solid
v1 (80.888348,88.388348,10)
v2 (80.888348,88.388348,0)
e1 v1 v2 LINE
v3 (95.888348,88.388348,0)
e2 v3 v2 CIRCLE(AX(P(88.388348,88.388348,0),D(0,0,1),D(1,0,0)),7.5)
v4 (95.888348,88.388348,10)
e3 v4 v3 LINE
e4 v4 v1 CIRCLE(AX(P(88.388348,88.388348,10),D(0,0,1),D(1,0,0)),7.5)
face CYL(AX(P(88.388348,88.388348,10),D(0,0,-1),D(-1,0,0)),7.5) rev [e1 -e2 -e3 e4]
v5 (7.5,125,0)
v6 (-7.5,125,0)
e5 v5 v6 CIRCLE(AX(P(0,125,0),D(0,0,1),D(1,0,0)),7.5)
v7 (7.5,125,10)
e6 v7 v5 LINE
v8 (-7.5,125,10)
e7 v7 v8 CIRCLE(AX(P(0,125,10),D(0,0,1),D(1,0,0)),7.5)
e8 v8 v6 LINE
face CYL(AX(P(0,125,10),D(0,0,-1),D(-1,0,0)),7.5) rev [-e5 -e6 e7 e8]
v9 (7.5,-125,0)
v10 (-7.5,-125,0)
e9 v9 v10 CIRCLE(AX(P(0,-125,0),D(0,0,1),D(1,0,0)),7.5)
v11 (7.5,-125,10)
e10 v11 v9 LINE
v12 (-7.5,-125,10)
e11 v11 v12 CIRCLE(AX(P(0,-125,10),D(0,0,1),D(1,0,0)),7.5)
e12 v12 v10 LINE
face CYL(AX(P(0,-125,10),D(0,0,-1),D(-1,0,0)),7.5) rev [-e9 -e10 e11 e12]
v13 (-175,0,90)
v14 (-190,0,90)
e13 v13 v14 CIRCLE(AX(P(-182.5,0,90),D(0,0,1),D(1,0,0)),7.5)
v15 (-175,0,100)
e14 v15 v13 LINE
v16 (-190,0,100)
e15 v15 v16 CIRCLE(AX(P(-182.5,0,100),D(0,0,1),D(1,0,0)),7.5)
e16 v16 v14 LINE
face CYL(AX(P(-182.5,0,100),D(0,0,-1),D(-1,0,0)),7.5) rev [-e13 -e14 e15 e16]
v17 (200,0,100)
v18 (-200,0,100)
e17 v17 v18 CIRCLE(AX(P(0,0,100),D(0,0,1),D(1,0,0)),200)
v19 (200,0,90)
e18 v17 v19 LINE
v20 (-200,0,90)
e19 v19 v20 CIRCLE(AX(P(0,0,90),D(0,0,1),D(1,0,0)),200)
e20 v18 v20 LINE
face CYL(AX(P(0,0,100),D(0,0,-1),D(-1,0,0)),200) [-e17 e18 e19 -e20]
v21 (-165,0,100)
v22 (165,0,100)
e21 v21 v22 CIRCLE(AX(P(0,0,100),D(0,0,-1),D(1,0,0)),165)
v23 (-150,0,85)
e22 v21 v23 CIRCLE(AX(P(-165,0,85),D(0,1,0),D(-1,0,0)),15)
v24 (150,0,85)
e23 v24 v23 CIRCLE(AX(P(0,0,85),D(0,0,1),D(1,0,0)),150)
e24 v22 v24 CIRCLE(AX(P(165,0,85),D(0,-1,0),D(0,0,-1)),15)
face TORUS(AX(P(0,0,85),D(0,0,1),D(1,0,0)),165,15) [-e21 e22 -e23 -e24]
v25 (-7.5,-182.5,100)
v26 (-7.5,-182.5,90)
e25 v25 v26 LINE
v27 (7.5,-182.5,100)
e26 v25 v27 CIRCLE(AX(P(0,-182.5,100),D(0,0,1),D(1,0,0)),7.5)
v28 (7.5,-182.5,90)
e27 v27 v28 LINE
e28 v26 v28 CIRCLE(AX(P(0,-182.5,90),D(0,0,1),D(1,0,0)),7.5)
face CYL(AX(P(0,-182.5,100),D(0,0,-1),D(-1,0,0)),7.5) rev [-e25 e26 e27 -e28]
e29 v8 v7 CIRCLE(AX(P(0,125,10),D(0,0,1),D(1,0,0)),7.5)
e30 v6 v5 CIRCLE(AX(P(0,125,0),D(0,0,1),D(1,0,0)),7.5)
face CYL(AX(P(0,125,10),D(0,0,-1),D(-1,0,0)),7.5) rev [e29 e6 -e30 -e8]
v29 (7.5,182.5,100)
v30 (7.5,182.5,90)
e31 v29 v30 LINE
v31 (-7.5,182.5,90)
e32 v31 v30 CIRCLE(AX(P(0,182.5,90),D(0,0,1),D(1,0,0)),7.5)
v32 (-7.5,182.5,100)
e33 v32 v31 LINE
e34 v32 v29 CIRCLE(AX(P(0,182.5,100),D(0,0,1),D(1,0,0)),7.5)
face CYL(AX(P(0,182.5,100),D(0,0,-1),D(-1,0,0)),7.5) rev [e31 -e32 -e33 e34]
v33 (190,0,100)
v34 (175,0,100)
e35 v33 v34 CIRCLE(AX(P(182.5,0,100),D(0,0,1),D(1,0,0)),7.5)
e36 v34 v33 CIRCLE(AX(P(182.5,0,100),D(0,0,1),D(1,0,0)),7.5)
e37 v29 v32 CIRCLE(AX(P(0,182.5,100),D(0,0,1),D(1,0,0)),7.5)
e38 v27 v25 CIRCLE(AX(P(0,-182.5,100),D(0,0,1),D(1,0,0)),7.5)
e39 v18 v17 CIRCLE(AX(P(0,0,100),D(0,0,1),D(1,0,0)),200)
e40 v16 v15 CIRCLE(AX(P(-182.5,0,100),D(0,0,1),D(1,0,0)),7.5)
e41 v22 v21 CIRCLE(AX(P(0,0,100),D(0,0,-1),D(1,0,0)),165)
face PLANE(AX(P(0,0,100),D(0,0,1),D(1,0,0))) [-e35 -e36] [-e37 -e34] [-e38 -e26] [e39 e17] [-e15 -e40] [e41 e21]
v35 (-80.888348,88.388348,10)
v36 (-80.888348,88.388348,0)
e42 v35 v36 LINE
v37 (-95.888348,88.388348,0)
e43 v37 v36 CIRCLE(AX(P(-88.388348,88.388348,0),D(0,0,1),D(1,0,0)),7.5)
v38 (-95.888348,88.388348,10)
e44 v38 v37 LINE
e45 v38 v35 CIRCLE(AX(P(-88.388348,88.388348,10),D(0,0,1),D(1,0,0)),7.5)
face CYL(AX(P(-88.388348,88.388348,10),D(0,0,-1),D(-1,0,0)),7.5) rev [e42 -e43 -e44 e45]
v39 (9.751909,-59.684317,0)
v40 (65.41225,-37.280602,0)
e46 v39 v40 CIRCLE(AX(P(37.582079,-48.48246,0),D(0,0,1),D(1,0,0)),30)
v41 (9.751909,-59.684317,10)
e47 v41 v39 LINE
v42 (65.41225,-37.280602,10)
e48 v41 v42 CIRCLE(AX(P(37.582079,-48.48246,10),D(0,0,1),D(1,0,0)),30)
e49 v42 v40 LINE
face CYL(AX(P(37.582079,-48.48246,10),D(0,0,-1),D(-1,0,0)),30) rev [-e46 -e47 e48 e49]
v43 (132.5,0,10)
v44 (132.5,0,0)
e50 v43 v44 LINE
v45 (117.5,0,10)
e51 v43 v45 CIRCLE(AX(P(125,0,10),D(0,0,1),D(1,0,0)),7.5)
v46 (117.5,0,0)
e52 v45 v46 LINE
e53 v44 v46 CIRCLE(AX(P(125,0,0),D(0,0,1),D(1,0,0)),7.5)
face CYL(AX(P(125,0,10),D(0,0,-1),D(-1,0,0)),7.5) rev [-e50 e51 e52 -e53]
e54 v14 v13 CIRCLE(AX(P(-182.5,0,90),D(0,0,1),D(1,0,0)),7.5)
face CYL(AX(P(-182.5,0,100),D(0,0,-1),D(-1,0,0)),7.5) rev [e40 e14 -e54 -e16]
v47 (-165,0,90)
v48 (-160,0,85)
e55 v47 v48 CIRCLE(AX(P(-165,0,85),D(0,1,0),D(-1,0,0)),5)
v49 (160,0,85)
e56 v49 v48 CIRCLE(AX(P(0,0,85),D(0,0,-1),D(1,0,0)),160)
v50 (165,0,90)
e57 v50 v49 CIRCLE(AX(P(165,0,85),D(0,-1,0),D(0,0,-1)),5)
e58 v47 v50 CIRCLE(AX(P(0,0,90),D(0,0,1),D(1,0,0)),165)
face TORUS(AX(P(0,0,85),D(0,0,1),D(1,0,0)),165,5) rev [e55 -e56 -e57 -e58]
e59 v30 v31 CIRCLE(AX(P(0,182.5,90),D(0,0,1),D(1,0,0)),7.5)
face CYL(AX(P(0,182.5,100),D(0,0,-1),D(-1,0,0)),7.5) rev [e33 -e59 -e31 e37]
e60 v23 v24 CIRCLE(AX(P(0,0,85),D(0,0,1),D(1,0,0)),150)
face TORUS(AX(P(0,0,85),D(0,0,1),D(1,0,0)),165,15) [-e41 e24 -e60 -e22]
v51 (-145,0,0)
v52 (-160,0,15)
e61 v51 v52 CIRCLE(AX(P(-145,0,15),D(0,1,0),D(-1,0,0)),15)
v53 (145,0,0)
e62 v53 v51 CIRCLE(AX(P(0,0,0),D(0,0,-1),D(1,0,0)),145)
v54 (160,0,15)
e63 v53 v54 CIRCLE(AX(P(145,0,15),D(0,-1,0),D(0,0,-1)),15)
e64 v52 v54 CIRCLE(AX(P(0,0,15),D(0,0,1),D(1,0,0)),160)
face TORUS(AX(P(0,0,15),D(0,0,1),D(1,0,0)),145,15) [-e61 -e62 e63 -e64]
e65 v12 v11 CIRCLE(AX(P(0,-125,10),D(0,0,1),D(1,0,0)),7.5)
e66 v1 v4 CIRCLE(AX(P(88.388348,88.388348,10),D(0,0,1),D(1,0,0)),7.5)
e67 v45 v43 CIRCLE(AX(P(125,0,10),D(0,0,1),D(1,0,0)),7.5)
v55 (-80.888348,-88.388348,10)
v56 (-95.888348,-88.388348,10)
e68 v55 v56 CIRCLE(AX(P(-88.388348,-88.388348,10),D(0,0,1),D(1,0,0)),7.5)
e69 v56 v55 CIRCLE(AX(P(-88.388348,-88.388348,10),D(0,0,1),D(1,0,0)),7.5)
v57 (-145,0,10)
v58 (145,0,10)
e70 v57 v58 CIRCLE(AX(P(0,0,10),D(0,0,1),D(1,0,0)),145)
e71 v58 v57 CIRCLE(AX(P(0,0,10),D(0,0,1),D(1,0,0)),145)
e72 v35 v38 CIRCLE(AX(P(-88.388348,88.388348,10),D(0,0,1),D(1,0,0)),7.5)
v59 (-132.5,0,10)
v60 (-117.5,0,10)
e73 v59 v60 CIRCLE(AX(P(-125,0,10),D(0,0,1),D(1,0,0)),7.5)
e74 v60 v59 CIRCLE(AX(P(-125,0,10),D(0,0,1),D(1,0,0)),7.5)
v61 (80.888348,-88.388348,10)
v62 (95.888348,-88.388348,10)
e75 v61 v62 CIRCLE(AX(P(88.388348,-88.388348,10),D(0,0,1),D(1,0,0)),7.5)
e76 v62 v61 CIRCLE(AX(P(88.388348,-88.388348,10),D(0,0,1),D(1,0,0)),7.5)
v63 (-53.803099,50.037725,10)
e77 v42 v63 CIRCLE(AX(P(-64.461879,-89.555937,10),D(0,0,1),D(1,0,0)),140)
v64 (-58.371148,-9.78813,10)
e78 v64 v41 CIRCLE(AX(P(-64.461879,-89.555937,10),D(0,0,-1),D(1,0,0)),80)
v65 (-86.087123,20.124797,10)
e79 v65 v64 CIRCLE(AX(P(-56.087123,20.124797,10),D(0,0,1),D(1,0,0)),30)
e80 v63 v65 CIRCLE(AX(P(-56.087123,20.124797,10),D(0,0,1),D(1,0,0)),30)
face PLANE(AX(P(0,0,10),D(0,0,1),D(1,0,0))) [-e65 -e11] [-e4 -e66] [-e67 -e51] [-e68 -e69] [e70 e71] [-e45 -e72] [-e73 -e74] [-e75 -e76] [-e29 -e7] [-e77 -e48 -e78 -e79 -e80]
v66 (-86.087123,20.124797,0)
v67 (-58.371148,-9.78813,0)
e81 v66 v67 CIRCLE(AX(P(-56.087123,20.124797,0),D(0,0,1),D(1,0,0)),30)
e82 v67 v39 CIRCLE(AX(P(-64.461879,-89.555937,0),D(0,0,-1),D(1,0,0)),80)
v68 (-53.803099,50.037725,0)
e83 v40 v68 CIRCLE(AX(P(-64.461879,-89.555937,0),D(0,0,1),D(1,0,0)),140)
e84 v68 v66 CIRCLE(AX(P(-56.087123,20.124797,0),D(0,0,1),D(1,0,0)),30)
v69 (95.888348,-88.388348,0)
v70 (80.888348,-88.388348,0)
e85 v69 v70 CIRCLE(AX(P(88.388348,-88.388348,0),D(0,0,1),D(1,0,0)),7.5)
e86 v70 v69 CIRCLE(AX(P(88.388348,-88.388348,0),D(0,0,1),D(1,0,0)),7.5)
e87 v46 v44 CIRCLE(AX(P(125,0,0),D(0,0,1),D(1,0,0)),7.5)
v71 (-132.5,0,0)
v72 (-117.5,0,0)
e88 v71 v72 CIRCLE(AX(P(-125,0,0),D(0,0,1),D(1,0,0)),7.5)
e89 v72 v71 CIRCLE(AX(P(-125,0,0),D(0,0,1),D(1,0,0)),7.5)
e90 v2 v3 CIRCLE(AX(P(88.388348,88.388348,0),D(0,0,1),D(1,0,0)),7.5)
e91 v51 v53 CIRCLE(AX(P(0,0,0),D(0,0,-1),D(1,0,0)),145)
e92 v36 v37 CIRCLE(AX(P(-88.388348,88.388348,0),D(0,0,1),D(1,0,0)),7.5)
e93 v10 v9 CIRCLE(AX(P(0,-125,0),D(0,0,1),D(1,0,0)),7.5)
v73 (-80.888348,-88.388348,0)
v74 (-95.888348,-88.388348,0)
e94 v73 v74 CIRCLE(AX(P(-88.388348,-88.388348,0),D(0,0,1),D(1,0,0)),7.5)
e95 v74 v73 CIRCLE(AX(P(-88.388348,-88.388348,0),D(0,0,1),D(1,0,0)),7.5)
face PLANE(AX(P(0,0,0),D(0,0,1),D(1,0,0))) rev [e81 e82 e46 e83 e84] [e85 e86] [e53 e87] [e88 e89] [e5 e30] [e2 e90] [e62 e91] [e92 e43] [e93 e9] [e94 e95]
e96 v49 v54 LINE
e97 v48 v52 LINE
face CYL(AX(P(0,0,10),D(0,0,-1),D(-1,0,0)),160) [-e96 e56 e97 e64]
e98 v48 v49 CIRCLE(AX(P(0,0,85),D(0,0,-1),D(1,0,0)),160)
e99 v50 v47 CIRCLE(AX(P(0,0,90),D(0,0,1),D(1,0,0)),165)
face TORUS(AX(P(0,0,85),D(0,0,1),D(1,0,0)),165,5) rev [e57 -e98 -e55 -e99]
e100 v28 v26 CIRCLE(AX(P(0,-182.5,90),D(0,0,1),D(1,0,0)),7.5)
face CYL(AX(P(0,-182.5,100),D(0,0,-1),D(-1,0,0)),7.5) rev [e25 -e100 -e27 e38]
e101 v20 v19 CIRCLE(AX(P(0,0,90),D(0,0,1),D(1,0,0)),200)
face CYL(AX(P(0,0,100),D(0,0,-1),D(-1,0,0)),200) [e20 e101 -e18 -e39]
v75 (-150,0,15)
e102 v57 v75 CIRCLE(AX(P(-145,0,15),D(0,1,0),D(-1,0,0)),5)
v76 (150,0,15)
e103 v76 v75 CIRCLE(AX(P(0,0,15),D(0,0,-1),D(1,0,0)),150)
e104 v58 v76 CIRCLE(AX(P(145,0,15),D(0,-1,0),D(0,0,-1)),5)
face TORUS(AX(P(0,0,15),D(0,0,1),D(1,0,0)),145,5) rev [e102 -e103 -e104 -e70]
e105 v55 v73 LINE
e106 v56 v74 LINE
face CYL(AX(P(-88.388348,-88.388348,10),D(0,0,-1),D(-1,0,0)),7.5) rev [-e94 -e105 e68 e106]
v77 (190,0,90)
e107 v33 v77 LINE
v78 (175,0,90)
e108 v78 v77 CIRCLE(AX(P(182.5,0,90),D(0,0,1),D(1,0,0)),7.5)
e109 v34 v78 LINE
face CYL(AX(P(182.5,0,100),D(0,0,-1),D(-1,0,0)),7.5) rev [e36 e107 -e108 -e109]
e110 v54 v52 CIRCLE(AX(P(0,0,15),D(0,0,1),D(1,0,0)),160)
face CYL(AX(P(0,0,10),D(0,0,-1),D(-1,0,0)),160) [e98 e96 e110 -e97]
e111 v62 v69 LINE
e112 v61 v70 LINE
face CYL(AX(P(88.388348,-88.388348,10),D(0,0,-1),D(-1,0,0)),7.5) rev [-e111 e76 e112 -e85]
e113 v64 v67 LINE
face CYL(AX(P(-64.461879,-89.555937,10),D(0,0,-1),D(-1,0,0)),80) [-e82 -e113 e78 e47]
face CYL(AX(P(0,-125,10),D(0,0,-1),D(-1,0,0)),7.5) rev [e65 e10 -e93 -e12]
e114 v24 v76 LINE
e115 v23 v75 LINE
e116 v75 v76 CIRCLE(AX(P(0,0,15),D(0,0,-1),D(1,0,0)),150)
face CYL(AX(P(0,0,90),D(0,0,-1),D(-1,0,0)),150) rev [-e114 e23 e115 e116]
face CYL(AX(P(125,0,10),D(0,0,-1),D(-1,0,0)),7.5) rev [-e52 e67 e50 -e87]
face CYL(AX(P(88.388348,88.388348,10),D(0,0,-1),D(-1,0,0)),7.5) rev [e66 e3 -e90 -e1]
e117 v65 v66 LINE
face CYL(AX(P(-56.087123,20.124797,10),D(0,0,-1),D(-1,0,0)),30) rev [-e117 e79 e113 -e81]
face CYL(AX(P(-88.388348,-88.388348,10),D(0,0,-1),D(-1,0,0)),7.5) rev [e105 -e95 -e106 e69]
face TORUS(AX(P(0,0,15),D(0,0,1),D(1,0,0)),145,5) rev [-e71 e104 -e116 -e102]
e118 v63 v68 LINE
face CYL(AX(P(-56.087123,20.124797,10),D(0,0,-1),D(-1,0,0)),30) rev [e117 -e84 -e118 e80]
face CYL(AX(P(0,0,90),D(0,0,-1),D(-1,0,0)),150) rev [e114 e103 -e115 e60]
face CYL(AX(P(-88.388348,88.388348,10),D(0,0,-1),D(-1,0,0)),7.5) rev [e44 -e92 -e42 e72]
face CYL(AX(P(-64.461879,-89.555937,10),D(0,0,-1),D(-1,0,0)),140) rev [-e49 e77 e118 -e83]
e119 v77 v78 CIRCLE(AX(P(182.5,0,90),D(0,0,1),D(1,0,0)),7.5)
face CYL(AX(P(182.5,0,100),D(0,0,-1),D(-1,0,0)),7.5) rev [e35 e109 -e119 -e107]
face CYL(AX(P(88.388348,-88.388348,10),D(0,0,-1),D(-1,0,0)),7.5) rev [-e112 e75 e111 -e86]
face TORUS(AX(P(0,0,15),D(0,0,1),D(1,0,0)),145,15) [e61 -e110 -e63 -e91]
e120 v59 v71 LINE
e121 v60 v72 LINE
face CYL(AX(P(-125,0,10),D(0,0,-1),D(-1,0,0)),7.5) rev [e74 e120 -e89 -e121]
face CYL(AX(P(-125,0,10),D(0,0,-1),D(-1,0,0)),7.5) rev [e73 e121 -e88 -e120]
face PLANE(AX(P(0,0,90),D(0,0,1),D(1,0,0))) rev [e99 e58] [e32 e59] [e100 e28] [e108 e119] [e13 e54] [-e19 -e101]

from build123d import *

# Parameters (mm, degrees)
SKETCH1_R           = 160
SKETCH1_R_2         = 7.5
BOSS_EXTRUDE1_DEPTH = 10
SKETCH2_R           = 160
SKETCH2_R_2         = 150
BOSS_EXTRUDE2_DEPTH = 80
SKETCH3_R           = 200
SKETCH3_R_2         = 150
SKETCH3_R_3         = 7.5
BOSS_EXTRUDE3_DEPTH = 10
FILLET1_R           = 5
FILLET2_R           = 15


with BuildPart() as part:
    # Sketch1 → Boss-Extrude1 (new body)
    with BuildSketch(Plane.XY):
        Circle(SKETCH1_R)
        with Locations((0, 125)):
            Circle(SKETCH1_R_2, mode=Mode.SUBTRACT)
        with Locations((88.388347648, 88.388347648)):
            Circle(SKETCH1_R_2, mode=Mode.SUBTRACT)
        with Locations((125, 0)):
            Circle(SKETCH1_R_2, mode=Mode.SUBTRACT)
        with Locations((88.388347648, -88.388347648)):
            Circle(SKETCH1_R_2, mode=Mode.SUBTRACT)
        with Locations((0, -125)):
            Circle(SKETCH1_R_2, mode=Mode.SUBTRACT)
        with Locations((-88.388347648, -88.388347648)):
            Circle(SKETCH1_R_2, mode=Mode.SUBTRACT)
        with Locations((-125, 0)):
            Circle(SKETCH1_R_2, mode=Mode.SUBTRACT)
        with Locations((-88.388347648, 88.388347648)):
            Circle(SKETCH1_R_2, mode=Mode.SUBTRACT)
        with BuildLine():
            ThreePointArc((-53.803098946, 50.037724546), (-86.000050805, 22.408821364), (-58.371147623, -9.788130495))
            ThreePointArc((-58.371147623, -9.788130495), (-17.190203431, -25.016114851), (9.751908775, -59.684317313))
            ThreePointArc((9.751908775, -59.684317313), (48.783936726, -76.312630338), (65.412249751, -37.280602387))
            ThreePointArc((65.412249751, -37.280602387), (18.26355339, 23.388751922), (-53.803098946, 50.037724546))
        make_face(mode=Mode.SUBTRACT)
    extrude(amount=BOSS_EXTRUDE1_DEPTH)

    # Sketch2 → Boss-Extrude2 (add)
    with BuildSketch(Plane.XY.offset(10)):
        Circle(SKETCH2_R)
        Circle(SKETCH2_R_2, mode=Mode.SUBTRACT)
    extrude(amount=BOSS_EXTRUDE2_DEPTH)

    # Sketch3 → Boss-Extrude3 (add)
    with BuildSketch(Plane.XY.offset(90)):
        Circle(SKETCH3_R)
        Circle(SKETCH3_R_2, mode=Mode.SUBTRACT)
        with Locations((0, 182.5)):
            Circle(SKETCH3_R_3, mode=Mode.SUBTRACT)
        with Locations((182.5, 0)):
            Circle(SKETCH3_R_3, mode=Mode.SUBTRACT)
        with Locations((0, -182.5)):
            Circle(SKETCH3_R_3, mode=Mode.SUBTRACT)
        with Locations((-182.5, 0)):
            Circle(SKETCH3_R_3, mode=Mode.SUBTRACT)
    extrude(amount=BOSS_EXTRUDE3_DEPTH)

    # Fillet1
    fillet1_edges = [part.edges().sort_by_distance(p)[0] for p in [
        (-150, 0, 10),
        (-160, 0, 90),
    ]]
    fillet(fillet1_edges, radius=FILLET1_R)

    # Fillet2
    fillet2_edges = [part.edges().sort_by_distance(p)[0] for p in [
        (-160, 0, 0),
        (-150, 0, 100),
    ]]
    fillet(fillet2_edges, radius=FILLET2_R)


solid = part.part
